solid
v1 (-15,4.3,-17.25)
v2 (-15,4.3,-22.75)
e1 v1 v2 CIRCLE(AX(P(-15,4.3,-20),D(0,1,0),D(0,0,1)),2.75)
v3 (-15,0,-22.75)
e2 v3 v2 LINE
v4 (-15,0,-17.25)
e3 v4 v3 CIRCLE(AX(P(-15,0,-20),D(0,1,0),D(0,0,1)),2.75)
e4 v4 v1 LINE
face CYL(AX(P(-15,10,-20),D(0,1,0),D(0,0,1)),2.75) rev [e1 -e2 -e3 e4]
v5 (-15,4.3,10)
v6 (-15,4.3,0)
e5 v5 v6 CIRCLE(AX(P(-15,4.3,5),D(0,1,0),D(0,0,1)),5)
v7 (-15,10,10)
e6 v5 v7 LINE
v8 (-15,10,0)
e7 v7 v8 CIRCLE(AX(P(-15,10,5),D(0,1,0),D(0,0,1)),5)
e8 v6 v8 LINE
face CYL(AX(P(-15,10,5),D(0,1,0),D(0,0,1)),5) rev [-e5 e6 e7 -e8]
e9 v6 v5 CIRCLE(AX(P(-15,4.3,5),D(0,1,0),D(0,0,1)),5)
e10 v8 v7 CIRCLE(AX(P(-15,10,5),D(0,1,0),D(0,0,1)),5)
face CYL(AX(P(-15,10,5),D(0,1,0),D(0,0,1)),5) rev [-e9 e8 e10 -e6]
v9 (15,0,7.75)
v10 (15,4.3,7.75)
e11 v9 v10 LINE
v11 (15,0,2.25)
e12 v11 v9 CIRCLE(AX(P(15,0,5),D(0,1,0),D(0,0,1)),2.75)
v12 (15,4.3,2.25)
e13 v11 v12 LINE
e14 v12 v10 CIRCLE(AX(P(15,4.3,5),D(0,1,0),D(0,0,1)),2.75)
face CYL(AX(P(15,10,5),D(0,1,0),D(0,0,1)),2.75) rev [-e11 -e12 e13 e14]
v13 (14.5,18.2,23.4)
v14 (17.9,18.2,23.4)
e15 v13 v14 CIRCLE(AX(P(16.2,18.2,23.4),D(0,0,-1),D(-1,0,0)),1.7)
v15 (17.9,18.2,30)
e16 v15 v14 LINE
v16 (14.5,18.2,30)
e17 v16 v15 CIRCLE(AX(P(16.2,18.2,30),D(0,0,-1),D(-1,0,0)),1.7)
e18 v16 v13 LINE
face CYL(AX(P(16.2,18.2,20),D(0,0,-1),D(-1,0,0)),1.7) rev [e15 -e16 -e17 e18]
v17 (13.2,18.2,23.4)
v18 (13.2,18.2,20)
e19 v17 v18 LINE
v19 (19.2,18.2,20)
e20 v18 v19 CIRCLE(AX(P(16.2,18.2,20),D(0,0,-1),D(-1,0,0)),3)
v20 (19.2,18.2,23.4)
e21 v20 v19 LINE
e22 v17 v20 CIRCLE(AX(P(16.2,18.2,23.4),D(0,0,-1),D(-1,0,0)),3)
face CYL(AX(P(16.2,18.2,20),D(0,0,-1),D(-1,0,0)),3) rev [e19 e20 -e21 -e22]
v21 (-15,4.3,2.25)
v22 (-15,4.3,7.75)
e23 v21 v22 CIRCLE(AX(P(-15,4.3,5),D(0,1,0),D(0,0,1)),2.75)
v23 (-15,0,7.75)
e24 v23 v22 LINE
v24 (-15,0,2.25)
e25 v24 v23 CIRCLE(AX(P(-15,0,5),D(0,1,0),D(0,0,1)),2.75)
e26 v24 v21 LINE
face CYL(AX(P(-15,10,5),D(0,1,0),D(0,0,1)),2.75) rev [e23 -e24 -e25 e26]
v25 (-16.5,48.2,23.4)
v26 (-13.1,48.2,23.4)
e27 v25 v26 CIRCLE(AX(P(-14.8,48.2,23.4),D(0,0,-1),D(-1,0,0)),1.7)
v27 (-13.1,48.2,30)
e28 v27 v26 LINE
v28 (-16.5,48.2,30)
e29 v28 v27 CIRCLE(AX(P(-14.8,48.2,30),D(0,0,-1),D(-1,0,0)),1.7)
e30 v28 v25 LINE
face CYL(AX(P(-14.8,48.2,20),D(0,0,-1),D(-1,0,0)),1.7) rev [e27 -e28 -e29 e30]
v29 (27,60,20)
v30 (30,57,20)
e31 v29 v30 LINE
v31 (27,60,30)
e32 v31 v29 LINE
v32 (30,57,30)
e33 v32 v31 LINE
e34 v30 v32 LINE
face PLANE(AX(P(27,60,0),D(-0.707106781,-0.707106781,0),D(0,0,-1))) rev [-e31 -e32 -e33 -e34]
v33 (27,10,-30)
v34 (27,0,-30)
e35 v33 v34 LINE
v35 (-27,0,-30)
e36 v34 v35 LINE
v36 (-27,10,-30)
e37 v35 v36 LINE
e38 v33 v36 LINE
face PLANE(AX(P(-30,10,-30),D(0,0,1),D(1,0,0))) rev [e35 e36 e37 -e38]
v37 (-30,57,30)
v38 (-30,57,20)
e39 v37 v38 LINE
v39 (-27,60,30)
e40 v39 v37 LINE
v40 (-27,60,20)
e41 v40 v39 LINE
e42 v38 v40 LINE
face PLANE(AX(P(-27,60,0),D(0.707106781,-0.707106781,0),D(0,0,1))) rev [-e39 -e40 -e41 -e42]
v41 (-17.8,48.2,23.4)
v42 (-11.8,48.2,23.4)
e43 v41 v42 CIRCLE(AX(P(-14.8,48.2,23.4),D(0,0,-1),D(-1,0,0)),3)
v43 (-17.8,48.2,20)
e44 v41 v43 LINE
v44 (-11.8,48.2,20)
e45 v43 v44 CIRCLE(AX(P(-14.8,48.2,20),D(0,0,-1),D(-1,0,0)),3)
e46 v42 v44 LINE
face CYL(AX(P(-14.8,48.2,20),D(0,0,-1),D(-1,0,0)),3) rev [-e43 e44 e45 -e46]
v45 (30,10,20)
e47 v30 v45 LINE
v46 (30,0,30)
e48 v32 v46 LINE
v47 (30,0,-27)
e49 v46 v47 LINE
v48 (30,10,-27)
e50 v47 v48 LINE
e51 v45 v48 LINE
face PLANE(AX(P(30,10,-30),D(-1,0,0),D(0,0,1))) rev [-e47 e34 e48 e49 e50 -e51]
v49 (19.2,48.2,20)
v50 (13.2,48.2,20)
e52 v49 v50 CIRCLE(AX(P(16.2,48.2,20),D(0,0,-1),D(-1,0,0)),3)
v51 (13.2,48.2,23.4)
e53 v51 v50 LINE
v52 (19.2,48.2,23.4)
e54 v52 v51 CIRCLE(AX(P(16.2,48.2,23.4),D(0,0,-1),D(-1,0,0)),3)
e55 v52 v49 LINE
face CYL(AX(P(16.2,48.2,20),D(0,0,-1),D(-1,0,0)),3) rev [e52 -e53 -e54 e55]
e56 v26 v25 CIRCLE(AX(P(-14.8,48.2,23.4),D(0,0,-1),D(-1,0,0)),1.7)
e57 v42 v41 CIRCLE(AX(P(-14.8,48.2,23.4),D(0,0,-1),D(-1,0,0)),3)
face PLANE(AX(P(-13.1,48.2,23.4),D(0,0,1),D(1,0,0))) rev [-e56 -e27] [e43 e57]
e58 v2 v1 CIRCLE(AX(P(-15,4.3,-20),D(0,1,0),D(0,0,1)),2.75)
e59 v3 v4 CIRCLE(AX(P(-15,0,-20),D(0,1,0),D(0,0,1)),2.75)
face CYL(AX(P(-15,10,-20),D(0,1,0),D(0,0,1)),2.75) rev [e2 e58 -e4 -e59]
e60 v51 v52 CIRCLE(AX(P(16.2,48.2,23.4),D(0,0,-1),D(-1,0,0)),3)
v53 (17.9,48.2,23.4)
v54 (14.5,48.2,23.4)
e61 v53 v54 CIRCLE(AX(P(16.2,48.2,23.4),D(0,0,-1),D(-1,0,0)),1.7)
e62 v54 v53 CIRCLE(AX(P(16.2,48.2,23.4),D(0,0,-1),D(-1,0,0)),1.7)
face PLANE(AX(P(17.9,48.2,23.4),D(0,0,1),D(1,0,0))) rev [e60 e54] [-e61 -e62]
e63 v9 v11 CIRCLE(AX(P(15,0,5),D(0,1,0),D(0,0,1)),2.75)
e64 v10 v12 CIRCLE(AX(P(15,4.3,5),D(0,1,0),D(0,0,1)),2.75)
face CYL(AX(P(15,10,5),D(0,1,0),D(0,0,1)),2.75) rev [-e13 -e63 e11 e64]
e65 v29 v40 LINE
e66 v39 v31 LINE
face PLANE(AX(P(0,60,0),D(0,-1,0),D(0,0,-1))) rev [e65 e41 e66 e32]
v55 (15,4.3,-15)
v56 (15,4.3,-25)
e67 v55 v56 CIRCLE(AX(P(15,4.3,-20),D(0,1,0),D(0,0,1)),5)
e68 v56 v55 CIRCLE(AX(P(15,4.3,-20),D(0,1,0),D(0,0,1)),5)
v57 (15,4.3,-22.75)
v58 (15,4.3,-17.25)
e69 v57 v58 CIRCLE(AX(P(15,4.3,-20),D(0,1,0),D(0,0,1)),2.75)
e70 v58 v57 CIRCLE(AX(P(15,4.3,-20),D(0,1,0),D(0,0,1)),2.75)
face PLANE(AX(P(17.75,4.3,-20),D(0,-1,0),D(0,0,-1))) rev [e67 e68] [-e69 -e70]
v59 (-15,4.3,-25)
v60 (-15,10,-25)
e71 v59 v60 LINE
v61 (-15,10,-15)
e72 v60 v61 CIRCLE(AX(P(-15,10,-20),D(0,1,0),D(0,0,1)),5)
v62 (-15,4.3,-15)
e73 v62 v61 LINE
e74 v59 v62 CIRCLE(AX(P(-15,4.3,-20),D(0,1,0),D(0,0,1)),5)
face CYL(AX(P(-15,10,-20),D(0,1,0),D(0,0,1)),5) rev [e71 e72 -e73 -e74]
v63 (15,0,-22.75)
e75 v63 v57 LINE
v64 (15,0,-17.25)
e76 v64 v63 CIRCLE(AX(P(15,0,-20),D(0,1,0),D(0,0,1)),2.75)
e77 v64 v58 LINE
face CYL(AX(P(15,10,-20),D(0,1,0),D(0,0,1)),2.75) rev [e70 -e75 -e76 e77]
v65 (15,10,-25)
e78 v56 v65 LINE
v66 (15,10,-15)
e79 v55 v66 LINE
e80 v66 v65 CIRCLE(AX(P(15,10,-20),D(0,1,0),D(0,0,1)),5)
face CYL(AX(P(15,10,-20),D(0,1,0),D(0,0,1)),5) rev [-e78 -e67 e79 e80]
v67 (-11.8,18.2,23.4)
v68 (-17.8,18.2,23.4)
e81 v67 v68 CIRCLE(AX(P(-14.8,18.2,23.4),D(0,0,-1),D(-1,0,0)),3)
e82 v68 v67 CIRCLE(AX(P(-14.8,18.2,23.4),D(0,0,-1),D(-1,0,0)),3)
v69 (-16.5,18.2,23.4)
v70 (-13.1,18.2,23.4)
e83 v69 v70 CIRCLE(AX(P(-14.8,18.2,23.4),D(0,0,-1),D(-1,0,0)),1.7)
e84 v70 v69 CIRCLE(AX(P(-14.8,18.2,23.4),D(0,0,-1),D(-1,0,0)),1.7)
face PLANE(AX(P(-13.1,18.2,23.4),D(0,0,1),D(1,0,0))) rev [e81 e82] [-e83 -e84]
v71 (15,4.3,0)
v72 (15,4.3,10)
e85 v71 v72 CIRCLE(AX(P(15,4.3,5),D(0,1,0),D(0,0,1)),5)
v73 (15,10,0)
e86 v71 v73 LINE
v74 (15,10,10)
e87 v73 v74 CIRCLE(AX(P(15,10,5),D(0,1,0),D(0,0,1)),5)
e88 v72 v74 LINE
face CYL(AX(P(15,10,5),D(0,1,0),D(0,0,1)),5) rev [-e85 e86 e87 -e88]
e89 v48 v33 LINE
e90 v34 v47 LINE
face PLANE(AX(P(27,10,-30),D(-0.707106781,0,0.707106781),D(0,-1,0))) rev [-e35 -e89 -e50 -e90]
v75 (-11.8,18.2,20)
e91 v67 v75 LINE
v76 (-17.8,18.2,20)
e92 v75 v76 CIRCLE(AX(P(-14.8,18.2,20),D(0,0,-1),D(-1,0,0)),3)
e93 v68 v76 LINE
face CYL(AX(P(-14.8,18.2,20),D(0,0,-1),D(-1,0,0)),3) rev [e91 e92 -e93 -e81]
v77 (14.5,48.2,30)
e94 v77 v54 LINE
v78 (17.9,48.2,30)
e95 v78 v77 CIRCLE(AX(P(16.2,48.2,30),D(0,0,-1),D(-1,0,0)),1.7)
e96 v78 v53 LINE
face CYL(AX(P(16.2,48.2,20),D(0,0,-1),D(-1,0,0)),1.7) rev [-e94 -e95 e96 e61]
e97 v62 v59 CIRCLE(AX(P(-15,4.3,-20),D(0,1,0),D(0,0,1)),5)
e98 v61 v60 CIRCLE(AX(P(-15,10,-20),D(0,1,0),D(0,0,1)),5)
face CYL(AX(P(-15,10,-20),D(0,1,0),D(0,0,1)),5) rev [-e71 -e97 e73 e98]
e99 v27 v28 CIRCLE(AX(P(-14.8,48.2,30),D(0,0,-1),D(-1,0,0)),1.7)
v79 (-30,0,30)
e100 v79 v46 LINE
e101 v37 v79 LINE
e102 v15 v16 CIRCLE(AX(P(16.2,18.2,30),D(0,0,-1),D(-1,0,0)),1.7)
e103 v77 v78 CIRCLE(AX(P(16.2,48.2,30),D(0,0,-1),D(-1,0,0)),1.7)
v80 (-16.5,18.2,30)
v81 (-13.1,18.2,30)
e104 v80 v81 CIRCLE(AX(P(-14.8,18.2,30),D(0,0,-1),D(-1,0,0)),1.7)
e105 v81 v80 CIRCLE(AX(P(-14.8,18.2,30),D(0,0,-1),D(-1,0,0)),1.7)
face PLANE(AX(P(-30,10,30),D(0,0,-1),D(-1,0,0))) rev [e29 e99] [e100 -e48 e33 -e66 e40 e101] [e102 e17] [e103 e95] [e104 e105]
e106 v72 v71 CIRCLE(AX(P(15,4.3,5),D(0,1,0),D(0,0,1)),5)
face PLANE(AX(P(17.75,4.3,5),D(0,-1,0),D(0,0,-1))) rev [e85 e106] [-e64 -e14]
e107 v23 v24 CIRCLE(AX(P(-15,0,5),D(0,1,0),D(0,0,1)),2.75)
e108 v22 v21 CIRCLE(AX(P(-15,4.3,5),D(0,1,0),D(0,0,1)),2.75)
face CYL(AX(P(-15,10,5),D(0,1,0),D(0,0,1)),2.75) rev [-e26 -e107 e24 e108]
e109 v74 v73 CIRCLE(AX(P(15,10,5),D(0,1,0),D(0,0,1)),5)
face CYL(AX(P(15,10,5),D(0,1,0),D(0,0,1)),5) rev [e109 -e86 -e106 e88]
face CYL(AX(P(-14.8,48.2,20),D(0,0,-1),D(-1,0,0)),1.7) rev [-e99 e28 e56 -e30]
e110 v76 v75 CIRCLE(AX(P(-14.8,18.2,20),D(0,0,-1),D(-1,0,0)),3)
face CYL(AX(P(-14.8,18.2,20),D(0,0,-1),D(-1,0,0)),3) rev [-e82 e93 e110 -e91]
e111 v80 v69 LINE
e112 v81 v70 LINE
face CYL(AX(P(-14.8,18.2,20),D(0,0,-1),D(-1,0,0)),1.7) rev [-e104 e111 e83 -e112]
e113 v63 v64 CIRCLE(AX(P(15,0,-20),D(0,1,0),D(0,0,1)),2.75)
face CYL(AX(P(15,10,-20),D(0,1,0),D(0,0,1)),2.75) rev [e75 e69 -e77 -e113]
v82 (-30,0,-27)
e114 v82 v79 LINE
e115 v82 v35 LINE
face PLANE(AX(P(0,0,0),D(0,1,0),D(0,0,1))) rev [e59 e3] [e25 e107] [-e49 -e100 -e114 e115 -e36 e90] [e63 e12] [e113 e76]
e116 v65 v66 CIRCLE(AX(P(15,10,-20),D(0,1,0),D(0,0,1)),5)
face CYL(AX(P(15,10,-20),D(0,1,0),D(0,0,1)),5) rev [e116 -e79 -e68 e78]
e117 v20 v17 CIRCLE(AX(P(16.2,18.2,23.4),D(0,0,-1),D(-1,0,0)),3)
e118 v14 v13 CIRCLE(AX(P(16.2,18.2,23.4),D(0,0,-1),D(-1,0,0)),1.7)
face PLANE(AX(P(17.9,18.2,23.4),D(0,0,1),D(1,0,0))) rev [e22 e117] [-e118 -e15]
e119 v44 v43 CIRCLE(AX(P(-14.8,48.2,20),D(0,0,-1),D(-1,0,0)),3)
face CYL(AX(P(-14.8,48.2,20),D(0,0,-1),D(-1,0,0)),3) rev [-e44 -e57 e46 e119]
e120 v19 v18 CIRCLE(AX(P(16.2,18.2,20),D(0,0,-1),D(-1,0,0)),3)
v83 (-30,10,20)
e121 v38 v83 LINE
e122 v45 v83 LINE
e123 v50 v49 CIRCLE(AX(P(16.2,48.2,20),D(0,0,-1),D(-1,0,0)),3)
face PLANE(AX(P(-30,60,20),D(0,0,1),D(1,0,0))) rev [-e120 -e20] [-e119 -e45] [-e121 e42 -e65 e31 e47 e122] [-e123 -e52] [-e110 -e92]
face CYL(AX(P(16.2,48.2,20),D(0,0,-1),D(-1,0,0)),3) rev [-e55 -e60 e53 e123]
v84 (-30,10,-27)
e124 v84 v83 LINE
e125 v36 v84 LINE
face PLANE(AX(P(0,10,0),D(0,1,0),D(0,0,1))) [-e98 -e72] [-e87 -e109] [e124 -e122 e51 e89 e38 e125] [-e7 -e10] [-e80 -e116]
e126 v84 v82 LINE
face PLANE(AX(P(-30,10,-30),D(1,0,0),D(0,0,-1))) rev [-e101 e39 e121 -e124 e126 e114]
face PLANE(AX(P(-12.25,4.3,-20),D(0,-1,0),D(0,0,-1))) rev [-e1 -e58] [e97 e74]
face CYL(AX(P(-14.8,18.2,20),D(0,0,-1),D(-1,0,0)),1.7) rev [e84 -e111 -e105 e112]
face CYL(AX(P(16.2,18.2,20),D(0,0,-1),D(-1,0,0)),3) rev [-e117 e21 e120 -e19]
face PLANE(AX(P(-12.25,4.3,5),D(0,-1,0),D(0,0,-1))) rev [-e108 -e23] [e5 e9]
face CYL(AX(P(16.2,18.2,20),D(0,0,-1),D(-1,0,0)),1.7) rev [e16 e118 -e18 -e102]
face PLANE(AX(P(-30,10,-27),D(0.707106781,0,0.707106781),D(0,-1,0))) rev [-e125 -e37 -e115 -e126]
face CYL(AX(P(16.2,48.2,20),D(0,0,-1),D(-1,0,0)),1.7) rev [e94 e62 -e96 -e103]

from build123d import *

# Parameters (mm, degrees)
SKETCH_1_W                = 60
SKETCH_1_H                = 60
EXTRUDE_1_DEPTH           = 10
SKETCH_2_W                = 60
SKETCH_2_H                = 10
EXTRUDE_2_DEPTH           = 50
CHAMFER_1_SIZE            = 3
HOLE_WIZARD_1_D           = 5.5
HOLE_WIZARD_1_DEPTH       = 15
HOLE_WIZARD_1_CBORE_D     = 10
HOLE_WIZARD_1_CBORE_DEPTH = 5.7
HOLE_WIZARD_1_TIP         = 1.652366702
HOLE_WIZARD_2_D           = 3.4
HOLE_WIZARD_2_DEPTH       = 15
HOLE_WIZARD_2_CBORE_D     = 6
HOLE_WIZARD_2_CBORE_DEPTH = 3.4
HOLE_WIZARD_2_TIP         = 1.021463052


with BuildPart() as part:
    # 草图1 → 凸台-拉伸1 (new body)
    with BuildSketch(Plane(origin=(0, 0, 0), x_dir=(1, 0, 0), z_dir=(0, 1, 0))):
        Rectangle(SKETCH_1_W, SKETCH_1_H)
    extrude(amount=EXTRUDE_1_DEPTH)

    # 草图2 → 凸台-拉伸2 (add)
    with BuildSketch(Plane(origin=(0, 10, 0), x_dir=(1, 0, 0), z_dir=(0, 1, 0))):
        with Locations((0, -25)):
            Rectangle(SKETCH_2_W, SKETCH_2_H)
    extrude(amount=EXTRUDE_2_DEPTH)

    # 倒角1
    chamfer_1_edges = [part.edges().sort_by_distance(p)[0] for p in [
        (-30, 60, 25),
        (30, 60, 25),
        (-30, 5, -30),
        (30, 5, -30),
    ]]
    chamfer(chamfer_1_edges, length=CHAMFER_1_SIZE)

    # 打孔尺寸(%根据)内六角圆柱头螺钉的类型1
    with Locations(Plane(origin=(0, 10, 0), x_dir=(1, 0, 0), z_dir=(0, 1, 0))):
        with Locations((-15, 20), (15, 20), (-15, -5), (15, -5)):
            CounterBoreHole(HOLE_WIZARD_1_D / 2, HOLE_WIZARD_1_CBORE_D / 2, HOLE_WIZARD_1_CBORE_DEPTH, depth=HOLE_WIZARD_1_DEPTH)
            with Locations((0, 0, -(HOLE_WIZARD_1_DEPTH + HOLE_WIZARD_1_TIP / 2))):  # 118° drill point
                Cone(0, HOLE_WIZARD_1_D / 2, HOLE_WIZARD_1_TIP, mode=Mode.SUBTRACT)

    # 打孔尺寸(%根据)内六角圆柱头螺钉的类型2
    with Locations(Plane(origin=(0, 0, 20), x_dir=(-1, 0, 0), z_dir=(0, 0, -1))):
        with Locations((-16.2, 48.2), (14.8, 48.2), (-16.2, 18.2), (14.8, 18.2)):
            CounterBoreHole(HOLE_WIZARD_2_D / 2, HOLE_WIZARD_2_CBORE_D / 2, HOLE_WIZARD_2_CBORE_DEPTH, depth=HOLE_WIZARD_2_DEPTH)
            with Locations((0, 0, -(HOLE_WIZARD_2_DEPTH + HOLE_WIZARD_2_TIP / 2))):  # 118° drill point
                Cone(0, HOLE_WIZARD_2_D / 2, HOLE_WIZARD_2_TIP, mode=Mode.SUBTRACT)


solid = part.part
